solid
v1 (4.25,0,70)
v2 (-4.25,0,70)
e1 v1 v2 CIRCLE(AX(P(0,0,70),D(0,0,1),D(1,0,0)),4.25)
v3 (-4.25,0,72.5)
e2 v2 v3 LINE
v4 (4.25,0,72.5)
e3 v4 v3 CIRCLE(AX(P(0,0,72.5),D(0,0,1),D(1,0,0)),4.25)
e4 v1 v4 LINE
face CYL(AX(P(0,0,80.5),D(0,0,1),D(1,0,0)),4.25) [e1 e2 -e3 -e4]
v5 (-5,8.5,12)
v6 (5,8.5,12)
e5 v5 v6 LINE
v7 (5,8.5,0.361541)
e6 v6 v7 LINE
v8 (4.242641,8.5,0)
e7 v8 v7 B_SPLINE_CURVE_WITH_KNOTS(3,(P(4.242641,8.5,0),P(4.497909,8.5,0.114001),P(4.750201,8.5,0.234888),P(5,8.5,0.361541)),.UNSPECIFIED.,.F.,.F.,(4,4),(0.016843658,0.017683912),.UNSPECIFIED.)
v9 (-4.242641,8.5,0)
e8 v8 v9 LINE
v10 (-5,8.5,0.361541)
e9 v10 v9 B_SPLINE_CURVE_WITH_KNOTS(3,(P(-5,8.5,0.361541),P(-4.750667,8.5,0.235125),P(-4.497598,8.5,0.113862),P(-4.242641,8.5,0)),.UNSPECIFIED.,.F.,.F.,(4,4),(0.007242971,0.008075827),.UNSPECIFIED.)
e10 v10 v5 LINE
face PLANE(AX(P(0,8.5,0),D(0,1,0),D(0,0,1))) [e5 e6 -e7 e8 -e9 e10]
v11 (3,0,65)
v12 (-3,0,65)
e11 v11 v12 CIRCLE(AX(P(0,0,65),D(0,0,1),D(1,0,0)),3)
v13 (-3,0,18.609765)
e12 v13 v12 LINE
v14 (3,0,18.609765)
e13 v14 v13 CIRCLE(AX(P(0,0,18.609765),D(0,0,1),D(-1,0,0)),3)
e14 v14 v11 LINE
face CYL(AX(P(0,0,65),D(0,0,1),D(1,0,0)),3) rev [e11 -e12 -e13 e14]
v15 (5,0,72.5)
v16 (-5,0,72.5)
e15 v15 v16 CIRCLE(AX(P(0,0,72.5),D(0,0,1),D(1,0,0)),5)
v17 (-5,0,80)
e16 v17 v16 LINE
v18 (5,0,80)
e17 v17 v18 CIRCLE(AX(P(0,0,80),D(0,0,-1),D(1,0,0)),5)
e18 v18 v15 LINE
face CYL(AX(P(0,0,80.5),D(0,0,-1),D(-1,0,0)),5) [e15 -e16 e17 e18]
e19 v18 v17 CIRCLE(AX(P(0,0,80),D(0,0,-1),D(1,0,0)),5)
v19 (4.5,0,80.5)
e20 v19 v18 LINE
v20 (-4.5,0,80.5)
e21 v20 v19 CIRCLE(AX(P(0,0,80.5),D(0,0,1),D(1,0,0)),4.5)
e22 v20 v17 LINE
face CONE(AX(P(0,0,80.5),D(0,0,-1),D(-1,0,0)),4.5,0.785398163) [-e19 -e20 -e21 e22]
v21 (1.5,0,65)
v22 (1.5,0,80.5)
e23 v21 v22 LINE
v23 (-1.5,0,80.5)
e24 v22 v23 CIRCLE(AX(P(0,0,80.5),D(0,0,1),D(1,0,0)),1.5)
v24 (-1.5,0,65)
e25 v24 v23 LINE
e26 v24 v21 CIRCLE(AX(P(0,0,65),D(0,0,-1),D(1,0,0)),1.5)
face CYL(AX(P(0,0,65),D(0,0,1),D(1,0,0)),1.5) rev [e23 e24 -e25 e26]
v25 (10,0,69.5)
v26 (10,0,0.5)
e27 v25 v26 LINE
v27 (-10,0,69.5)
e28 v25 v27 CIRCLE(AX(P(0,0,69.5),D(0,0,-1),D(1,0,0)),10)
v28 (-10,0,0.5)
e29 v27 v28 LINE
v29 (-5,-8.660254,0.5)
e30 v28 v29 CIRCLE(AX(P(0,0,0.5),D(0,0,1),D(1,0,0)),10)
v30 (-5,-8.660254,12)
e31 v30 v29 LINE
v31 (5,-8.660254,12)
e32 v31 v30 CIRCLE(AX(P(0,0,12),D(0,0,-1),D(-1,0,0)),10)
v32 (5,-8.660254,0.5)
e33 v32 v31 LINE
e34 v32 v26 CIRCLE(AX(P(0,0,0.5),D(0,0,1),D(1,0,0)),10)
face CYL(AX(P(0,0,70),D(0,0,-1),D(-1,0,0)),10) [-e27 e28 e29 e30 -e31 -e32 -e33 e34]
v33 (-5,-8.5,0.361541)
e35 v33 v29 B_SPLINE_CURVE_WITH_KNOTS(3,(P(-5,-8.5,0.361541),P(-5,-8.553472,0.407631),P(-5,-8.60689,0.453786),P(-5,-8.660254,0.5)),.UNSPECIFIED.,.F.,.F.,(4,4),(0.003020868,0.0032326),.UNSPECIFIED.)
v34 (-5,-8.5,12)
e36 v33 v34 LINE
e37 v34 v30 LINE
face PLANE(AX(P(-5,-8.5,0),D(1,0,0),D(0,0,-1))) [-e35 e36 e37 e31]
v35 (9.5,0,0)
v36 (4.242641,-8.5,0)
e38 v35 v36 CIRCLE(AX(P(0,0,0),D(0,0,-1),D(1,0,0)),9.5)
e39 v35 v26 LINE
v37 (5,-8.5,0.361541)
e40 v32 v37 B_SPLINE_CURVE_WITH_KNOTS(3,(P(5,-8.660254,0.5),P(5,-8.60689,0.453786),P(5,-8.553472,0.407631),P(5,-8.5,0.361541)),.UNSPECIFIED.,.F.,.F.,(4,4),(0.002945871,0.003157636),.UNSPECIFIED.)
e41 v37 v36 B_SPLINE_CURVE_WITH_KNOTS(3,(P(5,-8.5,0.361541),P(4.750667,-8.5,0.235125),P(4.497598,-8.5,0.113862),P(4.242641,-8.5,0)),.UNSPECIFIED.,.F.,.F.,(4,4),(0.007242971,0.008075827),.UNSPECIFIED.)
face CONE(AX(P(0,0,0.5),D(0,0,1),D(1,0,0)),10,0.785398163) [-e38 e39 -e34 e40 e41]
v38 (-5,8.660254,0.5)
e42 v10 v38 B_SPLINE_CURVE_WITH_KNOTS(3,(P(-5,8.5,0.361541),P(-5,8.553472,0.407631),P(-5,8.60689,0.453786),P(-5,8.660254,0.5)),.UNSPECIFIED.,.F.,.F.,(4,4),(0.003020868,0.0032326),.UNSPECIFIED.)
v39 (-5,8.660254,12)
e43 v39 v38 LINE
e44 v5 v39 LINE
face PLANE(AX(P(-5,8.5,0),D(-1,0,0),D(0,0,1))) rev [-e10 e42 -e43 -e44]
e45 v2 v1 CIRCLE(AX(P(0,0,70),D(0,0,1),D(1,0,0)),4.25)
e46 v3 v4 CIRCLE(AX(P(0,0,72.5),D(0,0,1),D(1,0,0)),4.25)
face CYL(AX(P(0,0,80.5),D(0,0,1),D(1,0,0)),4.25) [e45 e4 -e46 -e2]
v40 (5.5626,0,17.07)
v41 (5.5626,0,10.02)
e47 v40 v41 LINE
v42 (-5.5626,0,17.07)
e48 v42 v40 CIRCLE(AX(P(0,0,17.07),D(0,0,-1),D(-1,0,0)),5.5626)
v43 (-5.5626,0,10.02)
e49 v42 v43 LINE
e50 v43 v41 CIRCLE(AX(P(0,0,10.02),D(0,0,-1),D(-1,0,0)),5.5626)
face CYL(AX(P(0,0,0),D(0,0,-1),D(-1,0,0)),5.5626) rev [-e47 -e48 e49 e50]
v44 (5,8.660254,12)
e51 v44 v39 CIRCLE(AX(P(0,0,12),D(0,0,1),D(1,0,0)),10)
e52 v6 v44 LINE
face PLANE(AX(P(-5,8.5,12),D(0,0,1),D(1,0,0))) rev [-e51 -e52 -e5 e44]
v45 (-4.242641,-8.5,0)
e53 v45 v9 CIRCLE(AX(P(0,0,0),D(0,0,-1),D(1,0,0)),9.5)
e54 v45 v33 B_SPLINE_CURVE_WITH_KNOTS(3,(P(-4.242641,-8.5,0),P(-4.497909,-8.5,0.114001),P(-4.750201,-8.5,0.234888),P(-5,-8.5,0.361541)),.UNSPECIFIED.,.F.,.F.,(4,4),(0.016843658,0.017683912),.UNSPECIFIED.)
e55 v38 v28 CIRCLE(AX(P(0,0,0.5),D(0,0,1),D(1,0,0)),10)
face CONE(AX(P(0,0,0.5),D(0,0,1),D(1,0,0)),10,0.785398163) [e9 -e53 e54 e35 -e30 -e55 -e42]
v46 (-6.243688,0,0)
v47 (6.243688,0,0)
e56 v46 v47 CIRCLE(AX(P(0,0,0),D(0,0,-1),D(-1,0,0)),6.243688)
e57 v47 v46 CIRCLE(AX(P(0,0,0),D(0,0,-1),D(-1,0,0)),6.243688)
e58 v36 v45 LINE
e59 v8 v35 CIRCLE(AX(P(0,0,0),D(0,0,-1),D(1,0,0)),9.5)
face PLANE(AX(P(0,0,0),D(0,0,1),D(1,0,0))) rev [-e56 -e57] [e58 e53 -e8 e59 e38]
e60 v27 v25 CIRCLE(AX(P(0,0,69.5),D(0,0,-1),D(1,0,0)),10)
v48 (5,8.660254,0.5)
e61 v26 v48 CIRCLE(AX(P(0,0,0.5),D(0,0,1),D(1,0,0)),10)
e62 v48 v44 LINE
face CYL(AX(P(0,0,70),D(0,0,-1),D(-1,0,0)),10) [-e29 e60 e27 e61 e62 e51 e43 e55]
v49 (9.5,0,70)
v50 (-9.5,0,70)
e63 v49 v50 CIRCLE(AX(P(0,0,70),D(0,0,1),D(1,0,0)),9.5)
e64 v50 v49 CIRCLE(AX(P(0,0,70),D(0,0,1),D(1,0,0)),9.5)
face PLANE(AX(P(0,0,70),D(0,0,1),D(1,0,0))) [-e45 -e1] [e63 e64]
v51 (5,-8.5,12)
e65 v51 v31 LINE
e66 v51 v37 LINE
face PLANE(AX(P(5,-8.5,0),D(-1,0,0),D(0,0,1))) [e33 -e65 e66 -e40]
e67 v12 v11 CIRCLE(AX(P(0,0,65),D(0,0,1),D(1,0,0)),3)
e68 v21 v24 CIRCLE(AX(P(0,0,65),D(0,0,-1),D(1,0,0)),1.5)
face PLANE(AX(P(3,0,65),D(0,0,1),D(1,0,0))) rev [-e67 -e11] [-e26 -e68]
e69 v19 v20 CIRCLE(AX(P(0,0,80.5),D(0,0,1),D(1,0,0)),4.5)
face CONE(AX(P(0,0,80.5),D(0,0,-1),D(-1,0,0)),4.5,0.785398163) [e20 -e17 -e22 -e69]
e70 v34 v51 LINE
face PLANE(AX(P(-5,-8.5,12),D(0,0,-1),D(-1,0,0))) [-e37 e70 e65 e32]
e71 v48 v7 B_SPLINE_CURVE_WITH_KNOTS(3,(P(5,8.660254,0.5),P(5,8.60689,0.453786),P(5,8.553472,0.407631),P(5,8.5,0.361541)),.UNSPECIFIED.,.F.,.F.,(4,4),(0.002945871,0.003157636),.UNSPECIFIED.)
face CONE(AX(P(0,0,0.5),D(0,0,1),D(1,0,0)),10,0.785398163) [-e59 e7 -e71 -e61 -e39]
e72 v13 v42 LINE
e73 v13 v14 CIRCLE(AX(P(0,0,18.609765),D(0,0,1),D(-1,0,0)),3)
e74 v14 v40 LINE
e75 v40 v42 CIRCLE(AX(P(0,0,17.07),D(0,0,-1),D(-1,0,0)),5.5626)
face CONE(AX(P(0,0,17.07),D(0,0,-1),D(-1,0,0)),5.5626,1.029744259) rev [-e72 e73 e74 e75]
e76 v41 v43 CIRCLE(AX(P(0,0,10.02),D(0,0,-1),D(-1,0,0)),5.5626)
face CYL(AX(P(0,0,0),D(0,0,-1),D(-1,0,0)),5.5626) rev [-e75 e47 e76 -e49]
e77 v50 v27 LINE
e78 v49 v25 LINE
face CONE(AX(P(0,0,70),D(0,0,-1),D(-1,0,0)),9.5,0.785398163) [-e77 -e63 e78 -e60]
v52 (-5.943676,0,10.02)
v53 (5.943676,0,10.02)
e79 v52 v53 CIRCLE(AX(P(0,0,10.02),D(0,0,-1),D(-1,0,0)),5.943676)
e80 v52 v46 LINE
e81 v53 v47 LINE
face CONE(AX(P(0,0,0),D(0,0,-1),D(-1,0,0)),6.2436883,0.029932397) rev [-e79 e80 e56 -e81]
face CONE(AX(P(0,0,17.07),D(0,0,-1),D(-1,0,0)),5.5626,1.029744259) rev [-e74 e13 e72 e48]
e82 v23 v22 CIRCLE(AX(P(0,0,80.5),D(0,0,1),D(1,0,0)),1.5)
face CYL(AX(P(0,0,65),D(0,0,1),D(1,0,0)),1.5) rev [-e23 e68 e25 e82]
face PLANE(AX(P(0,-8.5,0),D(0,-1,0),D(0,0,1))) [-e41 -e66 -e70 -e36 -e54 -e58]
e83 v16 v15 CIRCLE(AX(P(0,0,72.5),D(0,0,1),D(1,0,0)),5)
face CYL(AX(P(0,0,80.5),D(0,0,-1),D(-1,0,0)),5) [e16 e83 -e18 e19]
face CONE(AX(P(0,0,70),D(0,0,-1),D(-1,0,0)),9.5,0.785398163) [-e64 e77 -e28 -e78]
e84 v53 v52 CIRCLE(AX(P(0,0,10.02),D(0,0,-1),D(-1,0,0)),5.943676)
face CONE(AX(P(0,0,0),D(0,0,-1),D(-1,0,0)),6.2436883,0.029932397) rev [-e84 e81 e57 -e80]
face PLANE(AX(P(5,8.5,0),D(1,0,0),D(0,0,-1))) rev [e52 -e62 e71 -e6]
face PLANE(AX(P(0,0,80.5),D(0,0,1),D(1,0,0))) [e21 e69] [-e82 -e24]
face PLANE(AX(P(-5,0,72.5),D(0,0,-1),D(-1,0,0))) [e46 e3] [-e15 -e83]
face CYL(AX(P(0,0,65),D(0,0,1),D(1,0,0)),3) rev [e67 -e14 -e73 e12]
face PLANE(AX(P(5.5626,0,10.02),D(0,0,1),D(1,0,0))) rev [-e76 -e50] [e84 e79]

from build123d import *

# Parameters (mm, degrees)
SKETCH_1_R                 = 10
EXTRUDE_1_DEPTH            = 70
SKETCH_2_R                 = 5
EXTRUDE_2_DEPTH            = 10.5
SKETCH_3_W                 = 0.75
SKETCH_3_H                 = 2.5
SKETCH_4_R                 = 1.5
CUT_EXTRUDE_1_DEPTH        = 15.5
HOLE_WIZARD_6_0_6_1_REACH  = 68.521
HOLE_WIZARD_6_0_6_1_BORE_R = 3
CHAMFER_1_SIZE             = 0.5
SKETCH_9_W                 = 10
SKETCH_9_H                 = 12
CUT_EXTRUDE_2_DEPTH        = 1.5


with BuildPart() as part:
    # 草图1 → 凸台-拉伸1 (new body)
    with BuildSketch(Plane.XY):
        Circle(SKETCH_1_R)
    extrude(amount=EXTRUDE_1_DEPTH)

    # 草图2 → 凸台-拉伸2 (add)
    with BuildSketch(Plane.XY.offset(70)):
        with Locations(Location((0, 0, 0), (0, 0, 180))):
            Circle(SKETCH_2_R)
    extrude(amount=EXTRUDE_2_DEPTH)

    # 草图3 → 切除-旋转1 (revolve, cut)
    with BuildSketch(Plane(origin=(0, 0, 0), x_dir=(1, 0, 0), z_dir=(0, 1, 0)), mode=Mode.PRIVATE) as cut_revolve_1_sk:
        with Locations((-4.625, -71.25)):
            Rectangle(SKETCH_3_W, SKETCH_3_H)
    revolve(cut_revolve_1_sk.sketch.rotate(Axis((0, 0, 80.5), (0, 0, -1)), 180), axis=Axis((0, 0, 80.5), (0, 0, -1)), mode=Mode.SUBTRACT)

    # 草图4 → 切除-拉伸1 (cut)
    with BuildSketch(Plane.XY.offset(80.5)):
        Circle(SKETCH_4_R)
    extrude(amount=-CUT_EXTRUDE_1_DEPTH, mode=Mode.SUBTRACT)

    # 草图5 → 1/4 NPT 螺纹孔1 (revolve, cut)
    with BuildSketch(Plane.YZ):
        Polygon((0, 0), (0, 20.412347279), (5.5626, 17.07), (5.5626, 10.02), (5.943676082, 10.02), (6.2436883, 0), align=None)
    revolve(axis=Axis((0, 0, -6.35), (0, 0, 1)), mode=Mode.SUBTRACT)

    # Ø6.0 (6) 直径孔1 bore → Ø6.0 (6) 直径孔1 (cut, up to next)
    with BuildSketch(Plane.XY.offset(65), mode=Mode.PRIVATE) as hole_wizard_6_0_6_1_sk1:
        Circle(HOLE_WIZARD_6_0_6_1_BORE_R)
    hole_wizard_6_0_6_1_tool1 = extrude(hole_wizard_6_0_6_1_sk1.sketch, amount=-HOLE_WIZARD_6_0_6_1_REACH, mode=Mode.PRIVATE) & part.part
    add(hole_wizard_6_0_6_1_tool1.solids().sort_by_distance((0, 0, 65))[0], mode=Mode.SUBTRACT)

    # 倒角1
    chamfer_1_edges = [part.edges().sort_by_distance(p)[0] for p in [
        (-10, 0, 0),
        (-10, 0, 70),
        (5, 0, 80.5),
    ]]
    chamfer(chamfer_1_edges, length=CHAMFER_1_SIZE)

    # 草图9 → 切除-拉伸2 (cut)
    with BuildSketch(Plane(origin=(0, 10, 0), x_dir=(1, 0, 0), z_dir=(0, 1, 0))):
        with Locations((0, -6)):
            Rectangle(SKETCH_9_W, SKETCH_9_H)
    cut_extrude_2 = extrude(amount=-CUT_EXTRUDE_2_DEPTH, mode=Mode.SUBTRACT)

    # 镜向1: 切除-拉伸2 across plane
    add(cut_extrude_2.mirror(Plane.ZX), mode=Mode.SUBTRACT)


solid = part.part
